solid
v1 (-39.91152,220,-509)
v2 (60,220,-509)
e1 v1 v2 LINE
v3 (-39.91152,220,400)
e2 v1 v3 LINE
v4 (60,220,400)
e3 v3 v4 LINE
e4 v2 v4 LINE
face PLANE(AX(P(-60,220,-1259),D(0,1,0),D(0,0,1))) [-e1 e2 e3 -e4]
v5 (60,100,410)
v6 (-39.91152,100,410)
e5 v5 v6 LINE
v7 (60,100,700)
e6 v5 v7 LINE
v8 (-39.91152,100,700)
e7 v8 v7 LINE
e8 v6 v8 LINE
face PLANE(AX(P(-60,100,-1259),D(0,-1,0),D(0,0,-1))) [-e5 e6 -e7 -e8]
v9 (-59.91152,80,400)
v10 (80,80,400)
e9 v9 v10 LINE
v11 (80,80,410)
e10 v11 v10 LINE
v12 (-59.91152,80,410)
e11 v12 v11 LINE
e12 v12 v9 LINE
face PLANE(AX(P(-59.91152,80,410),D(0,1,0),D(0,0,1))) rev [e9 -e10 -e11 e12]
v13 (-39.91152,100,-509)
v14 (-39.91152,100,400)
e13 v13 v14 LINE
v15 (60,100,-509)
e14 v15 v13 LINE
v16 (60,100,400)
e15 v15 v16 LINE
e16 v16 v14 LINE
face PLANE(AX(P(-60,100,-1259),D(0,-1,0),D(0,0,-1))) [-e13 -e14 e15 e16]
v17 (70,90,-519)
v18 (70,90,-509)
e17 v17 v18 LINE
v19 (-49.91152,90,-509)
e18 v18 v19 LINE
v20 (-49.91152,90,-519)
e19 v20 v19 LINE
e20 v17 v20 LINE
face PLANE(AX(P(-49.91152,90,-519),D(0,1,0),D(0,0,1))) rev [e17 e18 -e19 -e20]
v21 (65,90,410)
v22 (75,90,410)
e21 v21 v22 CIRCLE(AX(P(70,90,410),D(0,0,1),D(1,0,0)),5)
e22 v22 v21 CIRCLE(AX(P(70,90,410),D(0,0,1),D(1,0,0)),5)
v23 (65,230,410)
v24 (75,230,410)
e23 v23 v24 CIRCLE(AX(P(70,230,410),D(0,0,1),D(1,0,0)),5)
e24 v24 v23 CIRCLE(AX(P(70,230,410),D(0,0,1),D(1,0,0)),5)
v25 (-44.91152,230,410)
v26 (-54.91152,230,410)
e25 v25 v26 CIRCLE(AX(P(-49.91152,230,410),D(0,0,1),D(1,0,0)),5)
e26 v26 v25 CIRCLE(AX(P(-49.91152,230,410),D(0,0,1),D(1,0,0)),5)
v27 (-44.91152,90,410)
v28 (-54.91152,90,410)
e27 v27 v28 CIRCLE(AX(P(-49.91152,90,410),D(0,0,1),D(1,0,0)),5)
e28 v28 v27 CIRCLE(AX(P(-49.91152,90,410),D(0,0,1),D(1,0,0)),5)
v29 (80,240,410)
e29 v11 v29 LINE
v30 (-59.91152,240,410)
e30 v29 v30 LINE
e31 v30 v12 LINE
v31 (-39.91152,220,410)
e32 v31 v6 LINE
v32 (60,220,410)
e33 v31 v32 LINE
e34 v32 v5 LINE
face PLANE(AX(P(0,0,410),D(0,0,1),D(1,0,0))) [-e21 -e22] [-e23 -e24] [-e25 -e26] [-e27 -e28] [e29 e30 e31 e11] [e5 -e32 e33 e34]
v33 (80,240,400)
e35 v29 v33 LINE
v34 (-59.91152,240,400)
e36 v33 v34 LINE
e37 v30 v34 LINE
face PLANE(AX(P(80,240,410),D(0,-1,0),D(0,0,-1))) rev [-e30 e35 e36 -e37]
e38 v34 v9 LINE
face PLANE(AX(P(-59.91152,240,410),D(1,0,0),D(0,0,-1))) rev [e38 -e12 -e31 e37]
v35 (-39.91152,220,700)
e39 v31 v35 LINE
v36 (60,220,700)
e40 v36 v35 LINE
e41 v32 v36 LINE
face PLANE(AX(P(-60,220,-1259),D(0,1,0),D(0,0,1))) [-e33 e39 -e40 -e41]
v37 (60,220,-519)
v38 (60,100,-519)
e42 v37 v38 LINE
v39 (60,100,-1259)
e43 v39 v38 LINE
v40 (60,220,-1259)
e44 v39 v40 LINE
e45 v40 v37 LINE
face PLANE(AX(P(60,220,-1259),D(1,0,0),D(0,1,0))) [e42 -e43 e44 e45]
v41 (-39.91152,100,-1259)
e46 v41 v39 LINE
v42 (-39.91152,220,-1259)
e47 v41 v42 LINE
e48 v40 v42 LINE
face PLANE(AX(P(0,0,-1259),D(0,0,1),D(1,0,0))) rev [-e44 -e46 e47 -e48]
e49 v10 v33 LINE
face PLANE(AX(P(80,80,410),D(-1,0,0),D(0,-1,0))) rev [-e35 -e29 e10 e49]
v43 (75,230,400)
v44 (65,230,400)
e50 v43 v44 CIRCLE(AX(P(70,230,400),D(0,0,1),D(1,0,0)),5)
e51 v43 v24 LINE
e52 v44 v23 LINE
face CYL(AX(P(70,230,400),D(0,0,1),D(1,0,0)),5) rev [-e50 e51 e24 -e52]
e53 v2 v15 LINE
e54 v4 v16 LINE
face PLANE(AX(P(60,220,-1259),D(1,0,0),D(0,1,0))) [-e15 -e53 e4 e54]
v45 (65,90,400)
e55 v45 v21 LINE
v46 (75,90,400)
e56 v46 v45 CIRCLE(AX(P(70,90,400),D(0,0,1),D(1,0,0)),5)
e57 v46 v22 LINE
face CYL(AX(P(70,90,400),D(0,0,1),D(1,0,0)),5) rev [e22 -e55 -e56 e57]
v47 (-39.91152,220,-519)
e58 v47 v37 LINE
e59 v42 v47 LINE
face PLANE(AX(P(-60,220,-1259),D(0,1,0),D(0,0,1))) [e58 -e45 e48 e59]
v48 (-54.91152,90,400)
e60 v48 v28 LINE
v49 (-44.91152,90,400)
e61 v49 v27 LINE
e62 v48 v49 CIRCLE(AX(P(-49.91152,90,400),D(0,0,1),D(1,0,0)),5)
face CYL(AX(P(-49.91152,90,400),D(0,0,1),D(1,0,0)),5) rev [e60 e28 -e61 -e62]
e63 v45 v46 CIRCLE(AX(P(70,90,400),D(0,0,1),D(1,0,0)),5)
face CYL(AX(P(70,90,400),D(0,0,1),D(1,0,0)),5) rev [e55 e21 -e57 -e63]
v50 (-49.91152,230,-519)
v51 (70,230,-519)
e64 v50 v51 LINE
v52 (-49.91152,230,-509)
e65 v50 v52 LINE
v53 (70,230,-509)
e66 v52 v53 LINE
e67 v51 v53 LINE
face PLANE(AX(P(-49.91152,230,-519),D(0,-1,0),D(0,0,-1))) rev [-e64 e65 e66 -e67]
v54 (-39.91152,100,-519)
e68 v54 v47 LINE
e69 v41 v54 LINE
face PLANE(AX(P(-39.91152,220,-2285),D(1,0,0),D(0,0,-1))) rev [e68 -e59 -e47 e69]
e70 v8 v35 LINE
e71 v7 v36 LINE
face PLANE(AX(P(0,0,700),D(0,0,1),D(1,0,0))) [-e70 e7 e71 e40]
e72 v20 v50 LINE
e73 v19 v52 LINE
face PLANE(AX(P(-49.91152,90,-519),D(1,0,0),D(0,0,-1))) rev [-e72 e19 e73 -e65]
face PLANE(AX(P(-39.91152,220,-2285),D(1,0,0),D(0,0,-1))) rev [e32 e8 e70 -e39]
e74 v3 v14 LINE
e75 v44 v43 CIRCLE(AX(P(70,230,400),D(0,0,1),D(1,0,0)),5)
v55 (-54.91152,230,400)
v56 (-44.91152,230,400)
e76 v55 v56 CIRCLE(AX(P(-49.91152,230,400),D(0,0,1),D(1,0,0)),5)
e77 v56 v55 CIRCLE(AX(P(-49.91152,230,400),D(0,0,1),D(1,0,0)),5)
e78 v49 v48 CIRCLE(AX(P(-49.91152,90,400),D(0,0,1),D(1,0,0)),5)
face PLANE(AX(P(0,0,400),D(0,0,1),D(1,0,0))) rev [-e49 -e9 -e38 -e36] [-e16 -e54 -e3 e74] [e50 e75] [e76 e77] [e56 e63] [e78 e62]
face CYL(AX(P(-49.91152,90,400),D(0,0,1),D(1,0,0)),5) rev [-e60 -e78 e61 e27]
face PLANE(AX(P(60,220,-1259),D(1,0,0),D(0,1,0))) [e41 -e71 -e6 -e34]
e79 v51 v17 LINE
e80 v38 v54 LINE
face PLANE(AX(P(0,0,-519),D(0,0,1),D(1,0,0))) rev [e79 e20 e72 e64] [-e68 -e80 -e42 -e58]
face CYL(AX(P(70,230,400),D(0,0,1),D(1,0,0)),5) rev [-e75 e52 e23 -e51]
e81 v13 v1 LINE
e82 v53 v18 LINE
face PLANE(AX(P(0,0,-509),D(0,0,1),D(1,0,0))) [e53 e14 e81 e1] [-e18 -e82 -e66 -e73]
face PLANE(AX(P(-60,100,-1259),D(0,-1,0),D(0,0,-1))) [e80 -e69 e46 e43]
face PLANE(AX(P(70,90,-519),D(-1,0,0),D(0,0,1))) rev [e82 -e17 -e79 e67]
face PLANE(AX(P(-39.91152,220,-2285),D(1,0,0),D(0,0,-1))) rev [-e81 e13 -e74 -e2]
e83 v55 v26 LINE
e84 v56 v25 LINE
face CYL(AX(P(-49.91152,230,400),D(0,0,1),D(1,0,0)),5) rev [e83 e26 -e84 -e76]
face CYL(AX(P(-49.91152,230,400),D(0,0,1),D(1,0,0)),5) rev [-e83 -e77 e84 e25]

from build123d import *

# Parameters (mm, degrees)
BOSS_EXTRUDE1_DEPTH      = 700
BOSS_EXTRUDE1_DEPTH_BACK = 1259
SKETCH1_W                = 120
SKETCH1_H                = 120
SKETCH2_W                = 20.088480041
SKETCH2_H                = 120
CUT_EXTRUDE1_DEPTH       = 2985
BOSS_EXTRUDE2_START      = -750
SKETCH3_W                = 119.911519959
SKETCH3_H                = 140
BOSS_EXTRUDE2_DEPTH      = 10
BOSS_EXTRUDE3_START      = -300
SKETCH4_W                = 139.911519959
SKETCH4_H                = 160
BOSS_EXTRUDE3_DEPTH      = 10
SKETCH5_R                = 5
CUT_EXTRUDE2_DEPTH       = 10


with BuildPart() as part:
    # Sketch1 → Boss-Extrude1 (new, two sides: drawn at the far end of the back side and taken through both)
    with BuildSketch(Plane.XY.offset(-BOSS_EXTRUDE1_DEPTH_BACK)):
        with Locations((0, 160)):
            Rectangle(SKETCH1_W, SKETCH1_H)
    extrude(amount=BOSS_EXTRUDE1_DEPTH + BOSS_EXTRUDE1_DEPTH_BACK)

    # Sketch2 → Cut-Extrude1 (cut)
    with BuildSketch(Plane.XY.offset(700)):
        with Locations((-49.95575998, 160)):
            Rectangle(SKETCH2_W, SKETCH2_H)
    extrude(amount=-CUT_EXTRUDE1_DEPTH, mode=Mode.SUBTRACT)

    # Sketch3 → Boss-Extrude2 (add)
    with BuildSketch(Plane(origin=(0, 0, -1259), x_dir=(-1, 0, 0), z_dir=(0, 0, -1)).offset(BOSS_EXTRUDE2_START)):
        with Locations((-10.04424002, 160)):
            Rectangle(SKETCH3_W, SKETCH3_H)
    extrude(amount=BOSS_EXTRUDE2_DEPTH)

    # Sketch4 → Boss-Extrude3 (add)
    with BuildSketch(Plane.XY.offset(700).offset(BOSS_EXTRUDE3_START)):
        with Locations((10.04424002, 160)):
            Rectangle(SKETCH4_W, SKETCH4_H)
    extrude(amount=BOSS_EXTRUDE3_DEPTH)

    # Sketch5 → Cut-Extrude2 (cut)
    with BuildSketch(Plane.XY.offset(410)):
        with Locations((70, 230)):
            Circle(SKETCH5_R)
        with Locations((70, 90)):
            Circle(SKETCH5_R)
        with Locations((-49.911519959, 90)):
            Circle(SKETCH5_R)
        with Locations((-49.911519959, 230)):
            Circle(SKETCH5_R)
    extrude(amount=-CUT_EXTRUDE2_DEPTH, mode=Mode.SUBTRACT)


solid = part.part
